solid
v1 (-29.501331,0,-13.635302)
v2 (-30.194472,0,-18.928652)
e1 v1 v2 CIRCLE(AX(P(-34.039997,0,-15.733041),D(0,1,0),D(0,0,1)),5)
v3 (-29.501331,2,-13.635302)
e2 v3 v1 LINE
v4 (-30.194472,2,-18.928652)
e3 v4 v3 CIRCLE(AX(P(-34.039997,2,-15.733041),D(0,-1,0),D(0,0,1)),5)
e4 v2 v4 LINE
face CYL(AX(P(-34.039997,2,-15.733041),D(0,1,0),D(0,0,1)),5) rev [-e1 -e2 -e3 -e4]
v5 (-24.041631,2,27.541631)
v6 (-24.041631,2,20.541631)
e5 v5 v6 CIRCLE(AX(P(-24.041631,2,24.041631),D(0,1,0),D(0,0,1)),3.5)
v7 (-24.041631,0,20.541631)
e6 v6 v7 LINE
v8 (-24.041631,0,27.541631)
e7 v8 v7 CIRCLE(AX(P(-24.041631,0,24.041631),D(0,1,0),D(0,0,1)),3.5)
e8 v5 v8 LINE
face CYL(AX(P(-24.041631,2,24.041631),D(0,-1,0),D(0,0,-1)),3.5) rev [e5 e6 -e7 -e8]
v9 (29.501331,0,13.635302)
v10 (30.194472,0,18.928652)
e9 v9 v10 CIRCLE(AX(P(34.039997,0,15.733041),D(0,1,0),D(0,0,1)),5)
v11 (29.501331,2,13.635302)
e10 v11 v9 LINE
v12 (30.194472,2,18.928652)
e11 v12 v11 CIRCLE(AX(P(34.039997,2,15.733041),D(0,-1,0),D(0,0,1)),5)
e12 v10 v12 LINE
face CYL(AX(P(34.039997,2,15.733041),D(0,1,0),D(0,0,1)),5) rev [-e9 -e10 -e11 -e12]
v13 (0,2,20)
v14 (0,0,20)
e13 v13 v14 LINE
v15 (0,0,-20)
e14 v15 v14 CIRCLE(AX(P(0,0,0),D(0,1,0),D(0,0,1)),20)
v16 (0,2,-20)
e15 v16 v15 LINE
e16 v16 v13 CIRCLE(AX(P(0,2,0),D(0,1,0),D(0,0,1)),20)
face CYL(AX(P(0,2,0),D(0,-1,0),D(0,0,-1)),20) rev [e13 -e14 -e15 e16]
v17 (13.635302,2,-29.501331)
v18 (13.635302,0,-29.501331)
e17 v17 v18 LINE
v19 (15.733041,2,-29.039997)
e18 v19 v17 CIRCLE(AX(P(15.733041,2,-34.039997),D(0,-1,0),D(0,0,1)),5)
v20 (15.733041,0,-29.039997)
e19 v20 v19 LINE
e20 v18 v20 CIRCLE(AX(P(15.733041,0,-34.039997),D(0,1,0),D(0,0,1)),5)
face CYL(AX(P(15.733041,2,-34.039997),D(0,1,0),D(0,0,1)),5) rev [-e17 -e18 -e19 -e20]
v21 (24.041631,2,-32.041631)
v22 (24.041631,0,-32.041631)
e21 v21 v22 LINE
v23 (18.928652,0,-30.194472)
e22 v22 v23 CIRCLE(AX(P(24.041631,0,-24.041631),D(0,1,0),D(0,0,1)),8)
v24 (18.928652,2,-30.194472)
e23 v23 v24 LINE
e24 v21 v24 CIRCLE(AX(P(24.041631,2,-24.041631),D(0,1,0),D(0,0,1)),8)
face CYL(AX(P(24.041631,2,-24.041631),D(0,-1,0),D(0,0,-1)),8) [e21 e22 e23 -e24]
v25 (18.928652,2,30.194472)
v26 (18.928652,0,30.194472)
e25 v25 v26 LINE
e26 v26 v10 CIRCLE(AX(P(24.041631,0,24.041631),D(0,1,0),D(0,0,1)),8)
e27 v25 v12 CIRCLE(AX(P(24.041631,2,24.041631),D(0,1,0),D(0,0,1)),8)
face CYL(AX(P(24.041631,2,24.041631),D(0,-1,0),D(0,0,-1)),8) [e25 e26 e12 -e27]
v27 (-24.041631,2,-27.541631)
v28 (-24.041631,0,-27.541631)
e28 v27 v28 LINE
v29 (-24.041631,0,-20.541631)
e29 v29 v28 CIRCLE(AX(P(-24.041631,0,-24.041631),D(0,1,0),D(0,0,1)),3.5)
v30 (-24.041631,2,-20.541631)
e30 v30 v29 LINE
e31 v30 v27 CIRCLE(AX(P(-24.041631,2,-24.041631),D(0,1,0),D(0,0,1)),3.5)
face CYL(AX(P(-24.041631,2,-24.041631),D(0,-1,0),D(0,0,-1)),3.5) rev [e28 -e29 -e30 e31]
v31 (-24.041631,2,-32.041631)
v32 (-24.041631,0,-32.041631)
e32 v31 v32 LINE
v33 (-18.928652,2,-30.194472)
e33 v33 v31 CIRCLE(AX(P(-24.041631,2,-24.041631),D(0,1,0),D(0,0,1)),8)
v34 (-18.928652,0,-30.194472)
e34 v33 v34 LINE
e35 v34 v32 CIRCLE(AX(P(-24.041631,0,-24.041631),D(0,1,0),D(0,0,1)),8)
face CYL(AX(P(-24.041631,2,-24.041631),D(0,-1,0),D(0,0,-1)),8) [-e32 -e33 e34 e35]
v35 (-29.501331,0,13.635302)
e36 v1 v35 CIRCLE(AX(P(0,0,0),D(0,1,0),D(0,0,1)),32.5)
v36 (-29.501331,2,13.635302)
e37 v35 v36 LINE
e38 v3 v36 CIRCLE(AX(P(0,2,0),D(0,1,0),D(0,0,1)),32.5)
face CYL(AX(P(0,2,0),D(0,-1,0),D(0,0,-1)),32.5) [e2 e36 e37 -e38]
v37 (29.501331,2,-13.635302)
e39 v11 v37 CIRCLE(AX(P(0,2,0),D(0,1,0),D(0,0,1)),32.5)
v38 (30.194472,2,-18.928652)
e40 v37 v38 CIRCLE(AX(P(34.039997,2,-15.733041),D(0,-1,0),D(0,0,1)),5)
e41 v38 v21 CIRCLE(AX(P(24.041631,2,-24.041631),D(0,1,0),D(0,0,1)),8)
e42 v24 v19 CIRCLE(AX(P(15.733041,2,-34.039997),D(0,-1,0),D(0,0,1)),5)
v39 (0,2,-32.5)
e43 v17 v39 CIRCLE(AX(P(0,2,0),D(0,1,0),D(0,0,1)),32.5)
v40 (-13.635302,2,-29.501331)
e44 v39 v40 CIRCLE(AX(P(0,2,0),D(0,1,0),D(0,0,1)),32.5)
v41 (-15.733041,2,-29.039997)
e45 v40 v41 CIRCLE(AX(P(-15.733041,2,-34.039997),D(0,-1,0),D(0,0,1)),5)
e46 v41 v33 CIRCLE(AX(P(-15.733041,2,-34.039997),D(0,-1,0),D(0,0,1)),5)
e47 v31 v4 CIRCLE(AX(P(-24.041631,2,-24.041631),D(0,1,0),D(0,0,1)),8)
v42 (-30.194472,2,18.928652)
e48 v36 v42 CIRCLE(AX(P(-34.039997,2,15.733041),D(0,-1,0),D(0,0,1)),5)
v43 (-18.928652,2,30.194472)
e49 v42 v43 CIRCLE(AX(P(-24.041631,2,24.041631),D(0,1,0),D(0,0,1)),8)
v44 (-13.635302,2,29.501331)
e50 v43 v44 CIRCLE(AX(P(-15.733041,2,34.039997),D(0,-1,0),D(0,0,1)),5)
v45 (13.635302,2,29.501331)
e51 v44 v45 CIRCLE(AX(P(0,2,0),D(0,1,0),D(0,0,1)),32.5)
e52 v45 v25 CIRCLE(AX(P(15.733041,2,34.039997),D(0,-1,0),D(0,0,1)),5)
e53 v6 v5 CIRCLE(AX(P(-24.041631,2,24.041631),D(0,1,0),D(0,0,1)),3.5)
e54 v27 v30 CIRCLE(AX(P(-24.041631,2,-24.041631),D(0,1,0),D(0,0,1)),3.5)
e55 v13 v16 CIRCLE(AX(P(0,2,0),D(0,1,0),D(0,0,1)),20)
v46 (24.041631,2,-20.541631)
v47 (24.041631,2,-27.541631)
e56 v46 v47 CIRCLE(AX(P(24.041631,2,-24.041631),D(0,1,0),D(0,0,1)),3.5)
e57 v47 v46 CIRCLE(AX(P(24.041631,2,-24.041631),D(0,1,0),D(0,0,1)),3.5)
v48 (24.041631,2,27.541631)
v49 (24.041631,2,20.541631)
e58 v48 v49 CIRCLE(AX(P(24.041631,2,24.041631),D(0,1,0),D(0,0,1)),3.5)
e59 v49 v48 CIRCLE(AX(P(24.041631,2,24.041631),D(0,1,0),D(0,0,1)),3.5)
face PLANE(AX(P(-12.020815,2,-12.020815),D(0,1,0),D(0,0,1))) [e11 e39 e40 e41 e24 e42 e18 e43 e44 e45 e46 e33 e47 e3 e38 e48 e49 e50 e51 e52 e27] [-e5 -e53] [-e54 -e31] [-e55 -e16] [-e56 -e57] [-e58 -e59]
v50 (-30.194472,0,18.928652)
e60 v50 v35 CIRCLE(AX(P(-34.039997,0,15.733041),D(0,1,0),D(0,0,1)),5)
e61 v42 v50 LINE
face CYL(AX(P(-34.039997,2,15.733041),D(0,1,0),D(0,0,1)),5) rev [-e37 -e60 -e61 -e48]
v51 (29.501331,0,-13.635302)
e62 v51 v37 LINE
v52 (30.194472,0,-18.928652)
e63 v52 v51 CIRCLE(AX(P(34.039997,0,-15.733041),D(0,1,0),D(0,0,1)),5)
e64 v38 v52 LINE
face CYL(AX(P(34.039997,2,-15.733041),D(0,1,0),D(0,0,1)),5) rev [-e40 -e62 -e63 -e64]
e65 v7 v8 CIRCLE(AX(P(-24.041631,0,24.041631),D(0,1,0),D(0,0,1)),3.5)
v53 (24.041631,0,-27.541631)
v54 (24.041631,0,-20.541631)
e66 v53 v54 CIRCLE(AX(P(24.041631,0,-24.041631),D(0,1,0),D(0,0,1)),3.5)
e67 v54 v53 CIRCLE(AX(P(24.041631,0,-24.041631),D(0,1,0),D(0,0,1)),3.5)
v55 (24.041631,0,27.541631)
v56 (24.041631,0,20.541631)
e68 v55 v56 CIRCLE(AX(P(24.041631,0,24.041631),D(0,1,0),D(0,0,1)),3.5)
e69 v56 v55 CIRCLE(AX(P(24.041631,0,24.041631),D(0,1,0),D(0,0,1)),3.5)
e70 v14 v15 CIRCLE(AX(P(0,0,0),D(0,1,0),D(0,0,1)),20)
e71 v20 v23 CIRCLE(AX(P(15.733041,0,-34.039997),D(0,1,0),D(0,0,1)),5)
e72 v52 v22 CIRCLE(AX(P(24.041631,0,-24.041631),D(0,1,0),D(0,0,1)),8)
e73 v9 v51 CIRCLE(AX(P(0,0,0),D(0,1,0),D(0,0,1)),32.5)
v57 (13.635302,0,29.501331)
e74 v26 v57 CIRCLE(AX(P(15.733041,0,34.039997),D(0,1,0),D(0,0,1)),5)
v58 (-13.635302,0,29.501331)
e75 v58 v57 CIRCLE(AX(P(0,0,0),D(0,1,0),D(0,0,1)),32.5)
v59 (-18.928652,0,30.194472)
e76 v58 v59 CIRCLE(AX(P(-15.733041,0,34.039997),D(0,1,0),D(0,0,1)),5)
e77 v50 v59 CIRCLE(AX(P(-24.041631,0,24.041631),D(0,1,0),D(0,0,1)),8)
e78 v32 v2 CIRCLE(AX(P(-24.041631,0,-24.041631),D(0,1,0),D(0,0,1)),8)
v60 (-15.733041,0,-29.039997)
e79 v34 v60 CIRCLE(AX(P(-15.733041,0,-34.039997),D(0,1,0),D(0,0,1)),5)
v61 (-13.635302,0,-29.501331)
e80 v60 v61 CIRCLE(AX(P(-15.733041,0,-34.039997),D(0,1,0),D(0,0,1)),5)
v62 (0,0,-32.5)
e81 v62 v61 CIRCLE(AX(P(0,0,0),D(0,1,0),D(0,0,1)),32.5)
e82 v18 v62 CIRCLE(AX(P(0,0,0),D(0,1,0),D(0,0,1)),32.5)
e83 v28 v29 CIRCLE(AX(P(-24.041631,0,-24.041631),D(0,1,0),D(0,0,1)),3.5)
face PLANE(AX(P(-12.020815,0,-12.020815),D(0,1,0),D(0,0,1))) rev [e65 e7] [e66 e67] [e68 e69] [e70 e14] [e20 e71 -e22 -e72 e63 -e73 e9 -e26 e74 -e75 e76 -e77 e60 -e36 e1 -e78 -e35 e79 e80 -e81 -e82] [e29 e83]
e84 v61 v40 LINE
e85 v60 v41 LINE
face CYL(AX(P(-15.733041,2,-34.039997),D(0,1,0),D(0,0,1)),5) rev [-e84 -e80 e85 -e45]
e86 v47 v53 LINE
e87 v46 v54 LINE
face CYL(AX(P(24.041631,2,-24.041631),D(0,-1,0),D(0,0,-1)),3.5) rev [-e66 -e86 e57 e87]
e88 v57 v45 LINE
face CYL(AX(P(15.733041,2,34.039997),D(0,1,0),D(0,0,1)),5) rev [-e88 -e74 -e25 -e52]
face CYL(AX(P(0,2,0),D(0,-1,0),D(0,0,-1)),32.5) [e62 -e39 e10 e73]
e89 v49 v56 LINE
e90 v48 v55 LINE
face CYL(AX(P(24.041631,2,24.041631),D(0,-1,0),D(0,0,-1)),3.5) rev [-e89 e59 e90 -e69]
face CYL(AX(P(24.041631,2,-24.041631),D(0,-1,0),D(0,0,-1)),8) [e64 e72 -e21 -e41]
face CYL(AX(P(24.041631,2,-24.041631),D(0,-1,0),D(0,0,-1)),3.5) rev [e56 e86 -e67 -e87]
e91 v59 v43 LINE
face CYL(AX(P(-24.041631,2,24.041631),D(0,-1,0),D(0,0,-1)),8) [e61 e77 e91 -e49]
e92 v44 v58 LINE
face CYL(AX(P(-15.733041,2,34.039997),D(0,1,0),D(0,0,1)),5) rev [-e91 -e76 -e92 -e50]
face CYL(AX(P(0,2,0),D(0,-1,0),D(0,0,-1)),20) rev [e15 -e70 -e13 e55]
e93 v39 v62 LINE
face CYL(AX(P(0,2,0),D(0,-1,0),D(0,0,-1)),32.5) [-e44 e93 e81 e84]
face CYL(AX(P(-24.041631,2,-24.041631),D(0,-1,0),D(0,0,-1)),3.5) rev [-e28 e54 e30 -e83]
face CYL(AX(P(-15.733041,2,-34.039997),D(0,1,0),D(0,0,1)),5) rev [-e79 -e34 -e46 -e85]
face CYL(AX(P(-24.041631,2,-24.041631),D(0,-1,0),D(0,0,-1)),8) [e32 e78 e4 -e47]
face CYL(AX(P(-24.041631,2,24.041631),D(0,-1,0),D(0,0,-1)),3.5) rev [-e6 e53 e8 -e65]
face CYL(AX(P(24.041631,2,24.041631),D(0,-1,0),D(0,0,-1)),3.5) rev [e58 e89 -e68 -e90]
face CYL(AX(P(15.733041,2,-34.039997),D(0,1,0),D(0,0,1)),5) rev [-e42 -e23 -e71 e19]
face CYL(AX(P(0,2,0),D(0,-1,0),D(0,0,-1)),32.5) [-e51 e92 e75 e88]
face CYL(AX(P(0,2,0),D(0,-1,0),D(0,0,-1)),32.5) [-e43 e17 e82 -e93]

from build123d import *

# Parameters (mm, degrees)
SKETCH2_R           = 20
SKETCH2_R_2         = 3.5
BOSS_EXTRUDE1_DEPTH = 2
FILLET1_R           = 5
FILLET2_R           = 5


with BuildPart() as part:
    # Sketch2 → Boss-Extrude1 (new body)
    with BuildSketch(Plane(origin=(0, 0, 0), x_dir=(1, 0, 0), z_dir=(0, 1, 0))):
        with BuildLine():
            ThreePointArc((-27.733348113, 16.944361965), (-32.5, 0), (-27.733348113, -16.944361965))
            ThreePointArc((-27.733348113, -16.944361965), (-29.69848481, -29.69848481), (-16.944361965, -27.733348113))
            ThreePointArc((-16.944361965, -27.733348113), (0, -32.5), (16.944361965, -27.733348113))
            ThreePointArc((16.944361965, -27.733348113), (29.69848481, -29.69848481), (27.733348113, -16.944361965))
            ThreePointArc((27.733348113, -16.944361965), (32.5, 0), (27.733348113, 16.944361965))
            ThreePointArc((27.733348113, 16.944361965), (29.69848481, 29.69848481), (16.944361965, 27.733348113))
            ThreePointArc((16.944361965, 27.733348113), (0, 32.5), (-16.944361965, 27.733348113))
            ThreePointArc((-16.944361965, 27.733348113), (-29.69848481, 29.69848481), (-27.733348113, 16.944361965))
        make_face()
        with Locations(Location((0, 0, 0), (0, 0, 270))):
            Circle(SKETCH2_R, mode=Mode.SUBTRACT)
        with Locations(Location((-24.04163056, 24.04163056, 0), (0, 0, 270))):
            Circle(SKETCH2_R_2, mode=Mode.SUBTRACT)
        with Locations(Location((24.04163056, 24.04163056, 0), (0, 0, 270))):
            Circle(SKETCH2_R_2, mode=Mode.SUBTRACT)
        with Locations(Location((24.04163056, -24.04163056, 0), (0, 0, 270))):
            Circle(SKETCH2_R_2, mode=Mode.SUBTRACT)
        with Locations(Location((-24.04163056, -24.04163056, 0), (0, 0, 270))):
            Circle(SKETCH2_R_2, mode=Mode.SUBTRACT)
    extrude(amount=BOSS_EXTRUDE1_DEPTH)

    # Fillet1
    fillet1_edges = [part.edges().sort_by_distance(p)[0] for p in [
        (16.944361965, 1, -27.733348113),
        (27.733348113, 1, -16.944361965),
        (27.733348113, 1, 16.944361965),
        (16.944361965, 1, 27.733348113),
        (-16.944361965, 1, 27.733348113),
        (-27.733348113, 1, 16.944361965),
        (-27.733348113, 1, -16.944361965),
    ]]
    fillet(fillet1_edges, radius=FILLET1_R)

    # Fillet2
    fillet2_edges = [part.edges().sort_by_distance(p)[0] for p in [
        (-16.944361965, 1, -27.733348113),
    ]]
    fillet(fillet2_edges, radius=FILLET2_R)


solid = part.part
